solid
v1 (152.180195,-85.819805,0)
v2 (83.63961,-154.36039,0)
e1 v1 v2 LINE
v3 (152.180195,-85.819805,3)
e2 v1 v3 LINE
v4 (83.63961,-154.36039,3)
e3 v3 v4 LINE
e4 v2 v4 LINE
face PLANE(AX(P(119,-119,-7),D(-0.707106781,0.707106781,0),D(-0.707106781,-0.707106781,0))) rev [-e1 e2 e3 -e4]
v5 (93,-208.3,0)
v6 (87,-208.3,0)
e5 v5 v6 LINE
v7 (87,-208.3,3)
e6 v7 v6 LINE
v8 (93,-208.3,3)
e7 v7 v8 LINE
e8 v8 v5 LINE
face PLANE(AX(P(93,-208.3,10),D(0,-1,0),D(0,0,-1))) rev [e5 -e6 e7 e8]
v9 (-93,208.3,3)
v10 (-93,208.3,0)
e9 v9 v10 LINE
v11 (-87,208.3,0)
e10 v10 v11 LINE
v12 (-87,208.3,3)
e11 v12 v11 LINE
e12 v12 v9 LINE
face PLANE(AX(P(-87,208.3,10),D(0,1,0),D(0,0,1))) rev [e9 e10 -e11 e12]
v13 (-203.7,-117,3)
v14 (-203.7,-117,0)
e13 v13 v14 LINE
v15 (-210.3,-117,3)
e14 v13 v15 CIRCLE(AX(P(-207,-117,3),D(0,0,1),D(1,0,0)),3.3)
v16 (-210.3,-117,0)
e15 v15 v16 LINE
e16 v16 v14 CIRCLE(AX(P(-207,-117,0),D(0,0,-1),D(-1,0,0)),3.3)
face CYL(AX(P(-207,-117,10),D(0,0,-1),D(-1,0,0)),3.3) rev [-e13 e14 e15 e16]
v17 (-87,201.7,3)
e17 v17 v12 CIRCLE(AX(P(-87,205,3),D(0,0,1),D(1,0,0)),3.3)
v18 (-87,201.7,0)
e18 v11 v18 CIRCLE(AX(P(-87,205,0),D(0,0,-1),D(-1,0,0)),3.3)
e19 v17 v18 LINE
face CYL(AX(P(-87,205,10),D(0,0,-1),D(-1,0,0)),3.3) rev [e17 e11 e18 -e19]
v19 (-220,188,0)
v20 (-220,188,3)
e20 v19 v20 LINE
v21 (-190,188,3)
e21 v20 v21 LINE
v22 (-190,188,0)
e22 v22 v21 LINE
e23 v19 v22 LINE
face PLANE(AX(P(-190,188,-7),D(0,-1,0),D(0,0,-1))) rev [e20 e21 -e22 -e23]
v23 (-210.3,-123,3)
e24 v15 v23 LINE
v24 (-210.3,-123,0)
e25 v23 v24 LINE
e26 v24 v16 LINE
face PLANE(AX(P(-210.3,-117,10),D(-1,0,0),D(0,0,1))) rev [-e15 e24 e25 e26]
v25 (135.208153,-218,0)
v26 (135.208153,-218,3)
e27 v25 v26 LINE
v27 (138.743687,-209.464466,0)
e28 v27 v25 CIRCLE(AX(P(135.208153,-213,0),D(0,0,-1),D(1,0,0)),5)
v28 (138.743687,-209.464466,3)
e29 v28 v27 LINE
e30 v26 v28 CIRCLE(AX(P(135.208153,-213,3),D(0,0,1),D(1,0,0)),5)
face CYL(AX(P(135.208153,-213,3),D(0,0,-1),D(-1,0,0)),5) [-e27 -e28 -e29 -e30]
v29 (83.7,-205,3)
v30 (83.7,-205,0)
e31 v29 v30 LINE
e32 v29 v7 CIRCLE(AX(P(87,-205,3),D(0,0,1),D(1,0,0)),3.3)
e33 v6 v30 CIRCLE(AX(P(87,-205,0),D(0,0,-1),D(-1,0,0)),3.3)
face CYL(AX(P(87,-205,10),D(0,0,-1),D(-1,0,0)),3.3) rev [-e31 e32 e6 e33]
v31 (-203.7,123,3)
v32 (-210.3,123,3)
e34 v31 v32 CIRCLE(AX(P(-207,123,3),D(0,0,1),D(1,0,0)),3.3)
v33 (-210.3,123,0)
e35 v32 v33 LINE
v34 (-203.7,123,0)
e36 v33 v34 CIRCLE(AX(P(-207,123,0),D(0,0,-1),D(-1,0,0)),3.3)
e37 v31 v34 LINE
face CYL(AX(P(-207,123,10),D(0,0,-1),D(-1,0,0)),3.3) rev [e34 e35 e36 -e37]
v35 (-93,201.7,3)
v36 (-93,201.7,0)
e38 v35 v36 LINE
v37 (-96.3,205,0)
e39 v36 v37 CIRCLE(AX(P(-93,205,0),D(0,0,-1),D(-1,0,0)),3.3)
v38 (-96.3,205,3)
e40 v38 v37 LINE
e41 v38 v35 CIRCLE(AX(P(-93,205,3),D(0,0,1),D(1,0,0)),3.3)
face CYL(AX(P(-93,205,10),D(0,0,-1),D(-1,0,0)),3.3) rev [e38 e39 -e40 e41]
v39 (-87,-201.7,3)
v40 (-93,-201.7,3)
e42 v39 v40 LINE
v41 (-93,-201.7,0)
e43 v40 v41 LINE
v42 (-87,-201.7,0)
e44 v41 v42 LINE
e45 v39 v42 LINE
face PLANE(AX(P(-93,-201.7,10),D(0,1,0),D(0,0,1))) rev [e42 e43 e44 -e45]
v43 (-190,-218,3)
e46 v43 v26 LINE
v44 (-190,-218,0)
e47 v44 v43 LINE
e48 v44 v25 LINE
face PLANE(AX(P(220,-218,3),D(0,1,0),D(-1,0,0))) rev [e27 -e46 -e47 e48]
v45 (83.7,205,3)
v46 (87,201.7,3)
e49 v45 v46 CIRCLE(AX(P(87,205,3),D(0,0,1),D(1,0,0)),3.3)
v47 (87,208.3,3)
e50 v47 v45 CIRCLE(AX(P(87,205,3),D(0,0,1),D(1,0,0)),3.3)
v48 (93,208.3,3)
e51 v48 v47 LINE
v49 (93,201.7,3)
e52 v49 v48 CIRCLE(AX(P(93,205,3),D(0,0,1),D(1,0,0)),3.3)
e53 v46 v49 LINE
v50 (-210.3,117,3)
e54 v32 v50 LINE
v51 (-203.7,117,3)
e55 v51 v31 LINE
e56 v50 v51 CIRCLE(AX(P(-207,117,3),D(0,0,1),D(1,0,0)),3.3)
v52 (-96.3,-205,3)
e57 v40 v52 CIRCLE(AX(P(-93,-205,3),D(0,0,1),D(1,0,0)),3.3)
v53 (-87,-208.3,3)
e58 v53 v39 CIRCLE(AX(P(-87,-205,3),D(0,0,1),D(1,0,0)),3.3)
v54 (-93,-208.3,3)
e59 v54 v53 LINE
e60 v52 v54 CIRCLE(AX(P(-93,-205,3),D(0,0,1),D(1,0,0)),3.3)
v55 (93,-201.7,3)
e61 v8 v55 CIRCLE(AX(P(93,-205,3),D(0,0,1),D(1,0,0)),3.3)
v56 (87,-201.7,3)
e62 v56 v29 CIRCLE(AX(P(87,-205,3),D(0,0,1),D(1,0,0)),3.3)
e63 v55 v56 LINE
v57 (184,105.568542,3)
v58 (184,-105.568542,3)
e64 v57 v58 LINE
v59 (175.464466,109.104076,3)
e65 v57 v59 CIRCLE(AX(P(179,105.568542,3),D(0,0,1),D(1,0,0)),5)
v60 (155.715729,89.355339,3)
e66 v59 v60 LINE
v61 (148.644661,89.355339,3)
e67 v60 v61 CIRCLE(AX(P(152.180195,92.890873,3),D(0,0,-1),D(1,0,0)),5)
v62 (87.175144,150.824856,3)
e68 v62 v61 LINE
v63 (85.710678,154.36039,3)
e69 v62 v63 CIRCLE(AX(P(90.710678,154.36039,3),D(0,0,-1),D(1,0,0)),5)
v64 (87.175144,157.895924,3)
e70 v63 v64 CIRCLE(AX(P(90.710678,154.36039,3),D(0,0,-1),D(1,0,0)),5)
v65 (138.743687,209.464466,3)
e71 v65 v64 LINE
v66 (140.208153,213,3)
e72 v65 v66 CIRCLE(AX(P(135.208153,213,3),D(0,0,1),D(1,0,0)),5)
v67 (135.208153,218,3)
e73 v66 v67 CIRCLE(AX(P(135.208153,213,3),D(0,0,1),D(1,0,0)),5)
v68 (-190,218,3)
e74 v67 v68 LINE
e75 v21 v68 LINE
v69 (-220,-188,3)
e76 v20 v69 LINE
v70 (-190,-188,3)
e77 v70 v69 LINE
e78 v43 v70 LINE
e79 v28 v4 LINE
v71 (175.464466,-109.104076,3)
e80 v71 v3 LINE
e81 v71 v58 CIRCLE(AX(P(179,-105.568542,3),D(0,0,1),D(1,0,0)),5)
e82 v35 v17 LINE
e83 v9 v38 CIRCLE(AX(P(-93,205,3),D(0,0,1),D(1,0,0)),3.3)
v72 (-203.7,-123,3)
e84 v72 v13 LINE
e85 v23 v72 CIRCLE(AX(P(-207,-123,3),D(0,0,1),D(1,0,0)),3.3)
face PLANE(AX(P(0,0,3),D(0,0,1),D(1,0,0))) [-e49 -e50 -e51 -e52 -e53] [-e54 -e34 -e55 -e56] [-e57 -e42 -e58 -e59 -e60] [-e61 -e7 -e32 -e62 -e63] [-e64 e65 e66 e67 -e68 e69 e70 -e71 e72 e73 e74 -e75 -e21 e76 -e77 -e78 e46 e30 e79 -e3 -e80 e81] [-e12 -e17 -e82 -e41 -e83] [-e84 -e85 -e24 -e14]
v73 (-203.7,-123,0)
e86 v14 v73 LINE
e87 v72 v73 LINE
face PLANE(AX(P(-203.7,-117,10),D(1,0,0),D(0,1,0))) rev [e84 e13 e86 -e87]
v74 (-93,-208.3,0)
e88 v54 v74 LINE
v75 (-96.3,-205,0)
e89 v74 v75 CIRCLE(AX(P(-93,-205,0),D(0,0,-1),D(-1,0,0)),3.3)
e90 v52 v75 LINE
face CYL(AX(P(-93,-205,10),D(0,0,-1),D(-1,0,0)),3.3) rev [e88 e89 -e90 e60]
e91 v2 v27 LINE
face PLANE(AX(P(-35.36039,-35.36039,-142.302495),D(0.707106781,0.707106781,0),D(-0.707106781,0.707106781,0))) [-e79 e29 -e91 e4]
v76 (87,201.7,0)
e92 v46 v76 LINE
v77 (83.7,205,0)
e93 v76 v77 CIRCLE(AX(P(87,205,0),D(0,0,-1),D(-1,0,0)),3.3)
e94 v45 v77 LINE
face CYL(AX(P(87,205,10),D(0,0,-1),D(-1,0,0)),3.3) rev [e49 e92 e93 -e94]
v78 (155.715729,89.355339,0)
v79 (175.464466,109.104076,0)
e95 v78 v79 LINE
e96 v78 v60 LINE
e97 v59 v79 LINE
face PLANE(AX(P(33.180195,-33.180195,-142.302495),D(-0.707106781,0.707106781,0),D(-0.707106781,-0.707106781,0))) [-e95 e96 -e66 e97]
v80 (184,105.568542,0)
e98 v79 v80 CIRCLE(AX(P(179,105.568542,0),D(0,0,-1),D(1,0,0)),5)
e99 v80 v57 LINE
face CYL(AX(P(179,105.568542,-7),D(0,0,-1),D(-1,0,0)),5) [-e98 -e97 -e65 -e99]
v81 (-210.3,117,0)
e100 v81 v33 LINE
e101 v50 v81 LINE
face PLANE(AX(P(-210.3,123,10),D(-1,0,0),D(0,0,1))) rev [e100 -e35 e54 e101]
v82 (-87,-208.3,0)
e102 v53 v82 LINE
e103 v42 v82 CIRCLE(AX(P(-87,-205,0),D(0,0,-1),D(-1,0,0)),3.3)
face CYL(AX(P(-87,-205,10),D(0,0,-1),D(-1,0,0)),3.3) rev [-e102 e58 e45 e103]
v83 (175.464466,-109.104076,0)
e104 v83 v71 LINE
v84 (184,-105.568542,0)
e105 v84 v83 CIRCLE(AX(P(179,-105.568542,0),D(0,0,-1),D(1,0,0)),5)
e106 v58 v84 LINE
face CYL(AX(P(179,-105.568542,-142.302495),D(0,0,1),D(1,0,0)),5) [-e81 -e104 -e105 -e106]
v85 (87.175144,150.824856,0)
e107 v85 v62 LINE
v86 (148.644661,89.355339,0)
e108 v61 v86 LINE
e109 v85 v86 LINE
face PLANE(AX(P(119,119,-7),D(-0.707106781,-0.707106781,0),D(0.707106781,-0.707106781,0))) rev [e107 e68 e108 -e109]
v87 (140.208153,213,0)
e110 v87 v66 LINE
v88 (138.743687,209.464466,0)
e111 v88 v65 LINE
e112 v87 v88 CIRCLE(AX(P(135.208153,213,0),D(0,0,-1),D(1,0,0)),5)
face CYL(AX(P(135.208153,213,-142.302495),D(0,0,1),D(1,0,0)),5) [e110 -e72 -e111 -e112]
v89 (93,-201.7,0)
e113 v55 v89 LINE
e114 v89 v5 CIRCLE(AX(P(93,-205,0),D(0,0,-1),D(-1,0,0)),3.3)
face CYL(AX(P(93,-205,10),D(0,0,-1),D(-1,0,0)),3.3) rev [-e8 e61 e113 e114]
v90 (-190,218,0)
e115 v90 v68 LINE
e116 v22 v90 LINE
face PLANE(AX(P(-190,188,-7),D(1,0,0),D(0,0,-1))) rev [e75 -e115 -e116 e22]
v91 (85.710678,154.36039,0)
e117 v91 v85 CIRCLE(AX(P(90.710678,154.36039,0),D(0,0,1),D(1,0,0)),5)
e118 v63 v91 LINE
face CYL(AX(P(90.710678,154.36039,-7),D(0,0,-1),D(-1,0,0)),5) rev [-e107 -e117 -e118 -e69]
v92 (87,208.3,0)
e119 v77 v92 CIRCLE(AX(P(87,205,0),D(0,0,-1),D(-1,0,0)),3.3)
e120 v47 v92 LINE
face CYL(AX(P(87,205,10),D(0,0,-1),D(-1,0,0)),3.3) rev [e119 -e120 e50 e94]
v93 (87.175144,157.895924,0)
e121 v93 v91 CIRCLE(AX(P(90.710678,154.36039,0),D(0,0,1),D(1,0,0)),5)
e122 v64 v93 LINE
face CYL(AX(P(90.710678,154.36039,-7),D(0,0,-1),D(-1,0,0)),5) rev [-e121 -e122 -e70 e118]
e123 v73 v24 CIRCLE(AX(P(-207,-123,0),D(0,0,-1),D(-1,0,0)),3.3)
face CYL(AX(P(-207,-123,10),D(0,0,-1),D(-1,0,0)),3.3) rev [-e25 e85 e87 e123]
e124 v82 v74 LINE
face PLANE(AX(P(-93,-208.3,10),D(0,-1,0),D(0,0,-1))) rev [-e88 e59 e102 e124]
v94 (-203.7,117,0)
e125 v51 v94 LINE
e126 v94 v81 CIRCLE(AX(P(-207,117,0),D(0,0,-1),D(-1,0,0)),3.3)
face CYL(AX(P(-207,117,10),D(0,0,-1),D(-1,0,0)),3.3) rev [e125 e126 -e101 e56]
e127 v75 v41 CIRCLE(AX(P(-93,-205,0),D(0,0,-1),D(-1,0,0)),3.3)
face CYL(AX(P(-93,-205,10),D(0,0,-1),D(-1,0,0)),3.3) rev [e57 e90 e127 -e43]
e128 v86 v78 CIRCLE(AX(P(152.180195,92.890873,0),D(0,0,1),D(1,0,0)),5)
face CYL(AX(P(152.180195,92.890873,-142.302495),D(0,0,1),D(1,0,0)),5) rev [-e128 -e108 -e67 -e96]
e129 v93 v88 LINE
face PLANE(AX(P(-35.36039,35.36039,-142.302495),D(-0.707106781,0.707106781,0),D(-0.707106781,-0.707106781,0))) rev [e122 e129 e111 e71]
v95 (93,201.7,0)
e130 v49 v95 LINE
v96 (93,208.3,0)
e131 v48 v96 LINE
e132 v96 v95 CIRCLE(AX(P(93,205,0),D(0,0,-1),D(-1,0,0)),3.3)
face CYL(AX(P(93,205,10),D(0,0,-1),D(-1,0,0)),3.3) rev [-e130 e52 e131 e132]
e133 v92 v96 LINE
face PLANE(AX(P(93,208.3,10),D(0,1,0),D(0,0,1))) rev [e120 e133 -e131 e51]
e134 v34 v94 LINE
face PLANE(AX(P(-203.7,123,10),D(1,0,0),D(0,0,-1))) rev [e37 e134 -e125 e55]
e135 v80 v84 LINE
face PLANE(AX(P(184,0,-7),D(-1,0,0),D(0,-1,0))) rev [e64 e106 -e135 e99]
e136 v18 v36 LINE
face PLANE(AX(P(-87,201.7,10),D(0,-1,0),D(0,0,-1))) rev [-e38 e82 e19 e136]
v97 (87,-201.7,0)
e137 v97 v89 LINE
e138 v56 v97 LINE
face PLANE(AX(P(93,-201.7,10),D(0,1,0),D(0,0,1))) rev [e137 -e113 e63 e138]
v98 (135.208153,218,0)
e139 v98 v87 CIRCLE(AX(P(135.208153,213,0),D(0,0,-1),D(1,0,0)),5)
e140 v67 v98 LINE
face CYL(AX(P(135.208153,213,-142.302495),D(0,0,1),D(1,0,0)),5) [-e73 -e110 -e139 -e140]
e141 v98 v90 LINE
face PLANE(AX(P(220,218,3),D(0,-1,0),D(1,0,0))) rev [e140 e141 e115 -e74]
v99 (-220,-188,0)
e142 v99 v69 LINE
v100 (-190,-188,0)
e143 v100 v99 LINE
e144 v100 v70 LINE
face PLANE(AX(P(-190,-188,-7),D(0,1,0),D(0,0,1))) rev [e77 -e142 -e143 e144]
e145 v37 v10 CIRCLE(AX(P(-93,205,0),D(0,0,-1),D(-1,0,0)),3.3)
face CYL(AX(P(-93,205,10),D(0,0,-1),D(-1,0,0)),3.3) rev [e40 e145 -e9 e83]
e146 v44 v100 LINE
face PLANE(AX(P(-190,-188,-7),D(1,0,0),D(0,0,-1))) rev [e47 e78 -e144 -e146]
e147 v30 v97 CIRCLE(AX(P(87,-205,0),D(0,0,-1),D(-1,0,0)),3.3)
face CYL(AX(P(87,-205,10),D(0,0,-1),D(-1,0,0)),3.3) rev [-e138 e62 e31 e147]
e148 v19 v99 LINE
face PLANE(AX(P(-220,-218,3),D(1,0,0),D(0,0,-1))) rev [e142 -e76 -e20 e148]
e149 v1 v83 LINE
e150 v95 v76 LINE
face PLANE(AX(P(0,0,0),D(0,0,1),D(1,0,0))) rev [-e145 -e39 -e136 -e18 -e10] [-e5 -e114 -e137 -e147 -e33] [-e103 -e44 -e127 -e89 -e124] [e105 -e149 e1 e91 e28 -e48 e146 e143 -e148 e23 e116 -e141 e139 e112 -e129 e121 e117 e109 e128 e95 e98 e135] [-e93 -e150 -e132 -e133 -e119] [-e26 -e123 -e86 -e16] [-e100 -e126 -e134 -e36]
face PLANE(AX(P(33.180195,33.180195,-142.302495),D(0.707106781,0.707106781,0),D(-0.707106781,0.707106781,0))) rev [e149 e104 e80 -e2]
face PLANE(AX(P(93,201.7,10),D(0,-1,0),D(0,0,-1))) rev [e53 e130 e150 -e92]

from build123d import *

# Parameters (mm, degrees)
SKETCH_1_W          = 440
SKETCH_1_H          = 436
EXTRUDE_1_DEPTH     = 3
SKETCH_2_W          = 30
SKETCH_2_H          = 30
CUT_EXTRUDE_1_DEPTH = 10
CUT_EXTRUDE_2_DEPTH = 10
CUT_EXTRUDE_3_DEPTH = 10
EXTRUDE_2_DEPTH     = 3
FILLET_1_R          = 5
CUT_EXTRUDE_4_DEPTH = 10


with BuildPart() as part:
    # 草图1 → 凸台-拉伸1 (new body)
    with BuildSketch(Plane.XY):
        Rectangle(SKETCH_1_W, SKETCH_1_H)
    extrude(amount=EXTRUDE_1_DEPTH)

    # 草图2 → 切除-拉伸1 (cut)
    with BuildSketch(Plane.XY.offset(3)):
        with Locations((-205, -203)):
            Rectangle(SKETCH_2_W, SKETCH_2_H)
        with Locations((-205, 203)):
            Rectangle(SKETCH_2_W, SKETCH_2_H)
    extrude(amount=-CUT_EXTRUDE_1_DEPTH, mode=Mode.SUBTRACT)

    # 草图3 → 切除-拉伸2 (cut)
    with BuildSketch(Plane.XY.offset(3)):
        Polygon((220, 218), (20, 218), (220, 18), align=None)
        Polygon((220, -218), (220, -18), (20, -218), align=None)
    extrude(amount=-CUT_EXTRUDE_2_DEPTH, mode=Mode.SUBTRACT)

    # 草图4 → 切除-拉伸3 (cut)
    with BuildSketch(Plane.XY.offset(3)):
        Polygon((220, 18), (184, 54), (184, -54), (220, -18), align=None)
    extrude(amount=-CUT_EXTRUDE_3_DEPTH, mode=Mode.SUBTRACT)

    # 草图5 → 凸台-拉伸2 (add)
    with BuildSketch(Plane.XY.offset(3)):
        Polygon((20, 218), (83.639610307, 154.360389693), (147.279220614, 218), align=None)
        Polygon((152.180194847, 85.819805153), (184, 54), (184, 117.639610307), align=None)
    extrude_2 = extrude(amount=-EXTRUDE_2_DEPTH)

    # 镜向1: 凸台-拉伸2 across plane
    add(extrude_2.mirror(Plane.ZX))

    # 圆角1
    fillet_1_edges = [part.edges().sort_by_distance(p)[0] for p in [
        (83.639610307, 154.360389693, 1.5),
        (147.279220614, 218, 1.5),
        (184, 117.639610307, 1.5),
        (152.180194847, 85.819805153, 1.5),
        (147.279220614, -218, 1.5),
        (184, -117.639610307, 1.5),
    ]]
    fillet(fillet_1_edges, radius=FILLET_1_R)

    # 草图6 → 切除-拉伸4 (cut)
    with BuildSketch(Plane(origin=(0, 0, 0), x_dir=(-1, 0, 0), z_dir=(0, 0, -1))):
        with BuildLine():
            Line((-93, 208.3), (-87, 208.3))
            ThreePointArc((-87, 208.3), (-83.7, 205), (-87, 201.7))
            Line((-87, 201.7), (-93, 201.7))
            ThreePointArc((-93, 201.7), (-96.3, 205), (-93, 208.3))
        make_face()
        with BuildLine():
            Line((87, 208.3), (93, 208.3))
            ThreePointArc((93, 208.3), (96.3, 205), (93, 201.7))
            Line((93, 201.7), (87, 201.7))
            ThreePointArc((87, 201.7), (83.7, 205), (87, 208.3))
        make_face()
        with BuildLine():
            Line((210.3, 123), (210.3, 117))
            ThreePointArc((210.3, 117), (207, 113.7), (203.7, 117))
            Line((203.7, 117), (203.7, 123))
            ThreePointArc((203.7, 123), (207, 126.3), (210.3, 123))
        make_face()
        with BuildLine():
            Line((210.3, -117), (210.3, -123))
            ThreePointArc((210.3, -123), (207, -126.3), (203.7, -123))
            Line((203.7, -123), (203.7, -117))
            ThreePointArc((203.7, -117), (207, -113.7), (210.3, -117))
        make_face()
        with BuildLine():
            Line((93, -208.3), (87, -208.3))
            ThreePointArc((87, -208.3), (83.7, -205), (87, -201.7))
            Line((87, -201.7), (93, -201.7))
            ThreePointArc((93, -201.7), (96.3, -205), (93, -208.3))
        make_face()
        with BuildLine():
            Line((-93, -201.7), (-87, -201.7))
            ThreePointArc((-87, -201.7), (-83.7, -205), (-87, -208.3))
            Line((-87, -208.3), (-93, -208.3))
            ThreePointArc((-93, -208.3), (-96.3, -205), (-93, -201.7))
        make_face()
    extrude(amount=-CUT_EXTRUDE_4_DEPTH, mode=Mode.SUBTRACT)


solid = part.part
